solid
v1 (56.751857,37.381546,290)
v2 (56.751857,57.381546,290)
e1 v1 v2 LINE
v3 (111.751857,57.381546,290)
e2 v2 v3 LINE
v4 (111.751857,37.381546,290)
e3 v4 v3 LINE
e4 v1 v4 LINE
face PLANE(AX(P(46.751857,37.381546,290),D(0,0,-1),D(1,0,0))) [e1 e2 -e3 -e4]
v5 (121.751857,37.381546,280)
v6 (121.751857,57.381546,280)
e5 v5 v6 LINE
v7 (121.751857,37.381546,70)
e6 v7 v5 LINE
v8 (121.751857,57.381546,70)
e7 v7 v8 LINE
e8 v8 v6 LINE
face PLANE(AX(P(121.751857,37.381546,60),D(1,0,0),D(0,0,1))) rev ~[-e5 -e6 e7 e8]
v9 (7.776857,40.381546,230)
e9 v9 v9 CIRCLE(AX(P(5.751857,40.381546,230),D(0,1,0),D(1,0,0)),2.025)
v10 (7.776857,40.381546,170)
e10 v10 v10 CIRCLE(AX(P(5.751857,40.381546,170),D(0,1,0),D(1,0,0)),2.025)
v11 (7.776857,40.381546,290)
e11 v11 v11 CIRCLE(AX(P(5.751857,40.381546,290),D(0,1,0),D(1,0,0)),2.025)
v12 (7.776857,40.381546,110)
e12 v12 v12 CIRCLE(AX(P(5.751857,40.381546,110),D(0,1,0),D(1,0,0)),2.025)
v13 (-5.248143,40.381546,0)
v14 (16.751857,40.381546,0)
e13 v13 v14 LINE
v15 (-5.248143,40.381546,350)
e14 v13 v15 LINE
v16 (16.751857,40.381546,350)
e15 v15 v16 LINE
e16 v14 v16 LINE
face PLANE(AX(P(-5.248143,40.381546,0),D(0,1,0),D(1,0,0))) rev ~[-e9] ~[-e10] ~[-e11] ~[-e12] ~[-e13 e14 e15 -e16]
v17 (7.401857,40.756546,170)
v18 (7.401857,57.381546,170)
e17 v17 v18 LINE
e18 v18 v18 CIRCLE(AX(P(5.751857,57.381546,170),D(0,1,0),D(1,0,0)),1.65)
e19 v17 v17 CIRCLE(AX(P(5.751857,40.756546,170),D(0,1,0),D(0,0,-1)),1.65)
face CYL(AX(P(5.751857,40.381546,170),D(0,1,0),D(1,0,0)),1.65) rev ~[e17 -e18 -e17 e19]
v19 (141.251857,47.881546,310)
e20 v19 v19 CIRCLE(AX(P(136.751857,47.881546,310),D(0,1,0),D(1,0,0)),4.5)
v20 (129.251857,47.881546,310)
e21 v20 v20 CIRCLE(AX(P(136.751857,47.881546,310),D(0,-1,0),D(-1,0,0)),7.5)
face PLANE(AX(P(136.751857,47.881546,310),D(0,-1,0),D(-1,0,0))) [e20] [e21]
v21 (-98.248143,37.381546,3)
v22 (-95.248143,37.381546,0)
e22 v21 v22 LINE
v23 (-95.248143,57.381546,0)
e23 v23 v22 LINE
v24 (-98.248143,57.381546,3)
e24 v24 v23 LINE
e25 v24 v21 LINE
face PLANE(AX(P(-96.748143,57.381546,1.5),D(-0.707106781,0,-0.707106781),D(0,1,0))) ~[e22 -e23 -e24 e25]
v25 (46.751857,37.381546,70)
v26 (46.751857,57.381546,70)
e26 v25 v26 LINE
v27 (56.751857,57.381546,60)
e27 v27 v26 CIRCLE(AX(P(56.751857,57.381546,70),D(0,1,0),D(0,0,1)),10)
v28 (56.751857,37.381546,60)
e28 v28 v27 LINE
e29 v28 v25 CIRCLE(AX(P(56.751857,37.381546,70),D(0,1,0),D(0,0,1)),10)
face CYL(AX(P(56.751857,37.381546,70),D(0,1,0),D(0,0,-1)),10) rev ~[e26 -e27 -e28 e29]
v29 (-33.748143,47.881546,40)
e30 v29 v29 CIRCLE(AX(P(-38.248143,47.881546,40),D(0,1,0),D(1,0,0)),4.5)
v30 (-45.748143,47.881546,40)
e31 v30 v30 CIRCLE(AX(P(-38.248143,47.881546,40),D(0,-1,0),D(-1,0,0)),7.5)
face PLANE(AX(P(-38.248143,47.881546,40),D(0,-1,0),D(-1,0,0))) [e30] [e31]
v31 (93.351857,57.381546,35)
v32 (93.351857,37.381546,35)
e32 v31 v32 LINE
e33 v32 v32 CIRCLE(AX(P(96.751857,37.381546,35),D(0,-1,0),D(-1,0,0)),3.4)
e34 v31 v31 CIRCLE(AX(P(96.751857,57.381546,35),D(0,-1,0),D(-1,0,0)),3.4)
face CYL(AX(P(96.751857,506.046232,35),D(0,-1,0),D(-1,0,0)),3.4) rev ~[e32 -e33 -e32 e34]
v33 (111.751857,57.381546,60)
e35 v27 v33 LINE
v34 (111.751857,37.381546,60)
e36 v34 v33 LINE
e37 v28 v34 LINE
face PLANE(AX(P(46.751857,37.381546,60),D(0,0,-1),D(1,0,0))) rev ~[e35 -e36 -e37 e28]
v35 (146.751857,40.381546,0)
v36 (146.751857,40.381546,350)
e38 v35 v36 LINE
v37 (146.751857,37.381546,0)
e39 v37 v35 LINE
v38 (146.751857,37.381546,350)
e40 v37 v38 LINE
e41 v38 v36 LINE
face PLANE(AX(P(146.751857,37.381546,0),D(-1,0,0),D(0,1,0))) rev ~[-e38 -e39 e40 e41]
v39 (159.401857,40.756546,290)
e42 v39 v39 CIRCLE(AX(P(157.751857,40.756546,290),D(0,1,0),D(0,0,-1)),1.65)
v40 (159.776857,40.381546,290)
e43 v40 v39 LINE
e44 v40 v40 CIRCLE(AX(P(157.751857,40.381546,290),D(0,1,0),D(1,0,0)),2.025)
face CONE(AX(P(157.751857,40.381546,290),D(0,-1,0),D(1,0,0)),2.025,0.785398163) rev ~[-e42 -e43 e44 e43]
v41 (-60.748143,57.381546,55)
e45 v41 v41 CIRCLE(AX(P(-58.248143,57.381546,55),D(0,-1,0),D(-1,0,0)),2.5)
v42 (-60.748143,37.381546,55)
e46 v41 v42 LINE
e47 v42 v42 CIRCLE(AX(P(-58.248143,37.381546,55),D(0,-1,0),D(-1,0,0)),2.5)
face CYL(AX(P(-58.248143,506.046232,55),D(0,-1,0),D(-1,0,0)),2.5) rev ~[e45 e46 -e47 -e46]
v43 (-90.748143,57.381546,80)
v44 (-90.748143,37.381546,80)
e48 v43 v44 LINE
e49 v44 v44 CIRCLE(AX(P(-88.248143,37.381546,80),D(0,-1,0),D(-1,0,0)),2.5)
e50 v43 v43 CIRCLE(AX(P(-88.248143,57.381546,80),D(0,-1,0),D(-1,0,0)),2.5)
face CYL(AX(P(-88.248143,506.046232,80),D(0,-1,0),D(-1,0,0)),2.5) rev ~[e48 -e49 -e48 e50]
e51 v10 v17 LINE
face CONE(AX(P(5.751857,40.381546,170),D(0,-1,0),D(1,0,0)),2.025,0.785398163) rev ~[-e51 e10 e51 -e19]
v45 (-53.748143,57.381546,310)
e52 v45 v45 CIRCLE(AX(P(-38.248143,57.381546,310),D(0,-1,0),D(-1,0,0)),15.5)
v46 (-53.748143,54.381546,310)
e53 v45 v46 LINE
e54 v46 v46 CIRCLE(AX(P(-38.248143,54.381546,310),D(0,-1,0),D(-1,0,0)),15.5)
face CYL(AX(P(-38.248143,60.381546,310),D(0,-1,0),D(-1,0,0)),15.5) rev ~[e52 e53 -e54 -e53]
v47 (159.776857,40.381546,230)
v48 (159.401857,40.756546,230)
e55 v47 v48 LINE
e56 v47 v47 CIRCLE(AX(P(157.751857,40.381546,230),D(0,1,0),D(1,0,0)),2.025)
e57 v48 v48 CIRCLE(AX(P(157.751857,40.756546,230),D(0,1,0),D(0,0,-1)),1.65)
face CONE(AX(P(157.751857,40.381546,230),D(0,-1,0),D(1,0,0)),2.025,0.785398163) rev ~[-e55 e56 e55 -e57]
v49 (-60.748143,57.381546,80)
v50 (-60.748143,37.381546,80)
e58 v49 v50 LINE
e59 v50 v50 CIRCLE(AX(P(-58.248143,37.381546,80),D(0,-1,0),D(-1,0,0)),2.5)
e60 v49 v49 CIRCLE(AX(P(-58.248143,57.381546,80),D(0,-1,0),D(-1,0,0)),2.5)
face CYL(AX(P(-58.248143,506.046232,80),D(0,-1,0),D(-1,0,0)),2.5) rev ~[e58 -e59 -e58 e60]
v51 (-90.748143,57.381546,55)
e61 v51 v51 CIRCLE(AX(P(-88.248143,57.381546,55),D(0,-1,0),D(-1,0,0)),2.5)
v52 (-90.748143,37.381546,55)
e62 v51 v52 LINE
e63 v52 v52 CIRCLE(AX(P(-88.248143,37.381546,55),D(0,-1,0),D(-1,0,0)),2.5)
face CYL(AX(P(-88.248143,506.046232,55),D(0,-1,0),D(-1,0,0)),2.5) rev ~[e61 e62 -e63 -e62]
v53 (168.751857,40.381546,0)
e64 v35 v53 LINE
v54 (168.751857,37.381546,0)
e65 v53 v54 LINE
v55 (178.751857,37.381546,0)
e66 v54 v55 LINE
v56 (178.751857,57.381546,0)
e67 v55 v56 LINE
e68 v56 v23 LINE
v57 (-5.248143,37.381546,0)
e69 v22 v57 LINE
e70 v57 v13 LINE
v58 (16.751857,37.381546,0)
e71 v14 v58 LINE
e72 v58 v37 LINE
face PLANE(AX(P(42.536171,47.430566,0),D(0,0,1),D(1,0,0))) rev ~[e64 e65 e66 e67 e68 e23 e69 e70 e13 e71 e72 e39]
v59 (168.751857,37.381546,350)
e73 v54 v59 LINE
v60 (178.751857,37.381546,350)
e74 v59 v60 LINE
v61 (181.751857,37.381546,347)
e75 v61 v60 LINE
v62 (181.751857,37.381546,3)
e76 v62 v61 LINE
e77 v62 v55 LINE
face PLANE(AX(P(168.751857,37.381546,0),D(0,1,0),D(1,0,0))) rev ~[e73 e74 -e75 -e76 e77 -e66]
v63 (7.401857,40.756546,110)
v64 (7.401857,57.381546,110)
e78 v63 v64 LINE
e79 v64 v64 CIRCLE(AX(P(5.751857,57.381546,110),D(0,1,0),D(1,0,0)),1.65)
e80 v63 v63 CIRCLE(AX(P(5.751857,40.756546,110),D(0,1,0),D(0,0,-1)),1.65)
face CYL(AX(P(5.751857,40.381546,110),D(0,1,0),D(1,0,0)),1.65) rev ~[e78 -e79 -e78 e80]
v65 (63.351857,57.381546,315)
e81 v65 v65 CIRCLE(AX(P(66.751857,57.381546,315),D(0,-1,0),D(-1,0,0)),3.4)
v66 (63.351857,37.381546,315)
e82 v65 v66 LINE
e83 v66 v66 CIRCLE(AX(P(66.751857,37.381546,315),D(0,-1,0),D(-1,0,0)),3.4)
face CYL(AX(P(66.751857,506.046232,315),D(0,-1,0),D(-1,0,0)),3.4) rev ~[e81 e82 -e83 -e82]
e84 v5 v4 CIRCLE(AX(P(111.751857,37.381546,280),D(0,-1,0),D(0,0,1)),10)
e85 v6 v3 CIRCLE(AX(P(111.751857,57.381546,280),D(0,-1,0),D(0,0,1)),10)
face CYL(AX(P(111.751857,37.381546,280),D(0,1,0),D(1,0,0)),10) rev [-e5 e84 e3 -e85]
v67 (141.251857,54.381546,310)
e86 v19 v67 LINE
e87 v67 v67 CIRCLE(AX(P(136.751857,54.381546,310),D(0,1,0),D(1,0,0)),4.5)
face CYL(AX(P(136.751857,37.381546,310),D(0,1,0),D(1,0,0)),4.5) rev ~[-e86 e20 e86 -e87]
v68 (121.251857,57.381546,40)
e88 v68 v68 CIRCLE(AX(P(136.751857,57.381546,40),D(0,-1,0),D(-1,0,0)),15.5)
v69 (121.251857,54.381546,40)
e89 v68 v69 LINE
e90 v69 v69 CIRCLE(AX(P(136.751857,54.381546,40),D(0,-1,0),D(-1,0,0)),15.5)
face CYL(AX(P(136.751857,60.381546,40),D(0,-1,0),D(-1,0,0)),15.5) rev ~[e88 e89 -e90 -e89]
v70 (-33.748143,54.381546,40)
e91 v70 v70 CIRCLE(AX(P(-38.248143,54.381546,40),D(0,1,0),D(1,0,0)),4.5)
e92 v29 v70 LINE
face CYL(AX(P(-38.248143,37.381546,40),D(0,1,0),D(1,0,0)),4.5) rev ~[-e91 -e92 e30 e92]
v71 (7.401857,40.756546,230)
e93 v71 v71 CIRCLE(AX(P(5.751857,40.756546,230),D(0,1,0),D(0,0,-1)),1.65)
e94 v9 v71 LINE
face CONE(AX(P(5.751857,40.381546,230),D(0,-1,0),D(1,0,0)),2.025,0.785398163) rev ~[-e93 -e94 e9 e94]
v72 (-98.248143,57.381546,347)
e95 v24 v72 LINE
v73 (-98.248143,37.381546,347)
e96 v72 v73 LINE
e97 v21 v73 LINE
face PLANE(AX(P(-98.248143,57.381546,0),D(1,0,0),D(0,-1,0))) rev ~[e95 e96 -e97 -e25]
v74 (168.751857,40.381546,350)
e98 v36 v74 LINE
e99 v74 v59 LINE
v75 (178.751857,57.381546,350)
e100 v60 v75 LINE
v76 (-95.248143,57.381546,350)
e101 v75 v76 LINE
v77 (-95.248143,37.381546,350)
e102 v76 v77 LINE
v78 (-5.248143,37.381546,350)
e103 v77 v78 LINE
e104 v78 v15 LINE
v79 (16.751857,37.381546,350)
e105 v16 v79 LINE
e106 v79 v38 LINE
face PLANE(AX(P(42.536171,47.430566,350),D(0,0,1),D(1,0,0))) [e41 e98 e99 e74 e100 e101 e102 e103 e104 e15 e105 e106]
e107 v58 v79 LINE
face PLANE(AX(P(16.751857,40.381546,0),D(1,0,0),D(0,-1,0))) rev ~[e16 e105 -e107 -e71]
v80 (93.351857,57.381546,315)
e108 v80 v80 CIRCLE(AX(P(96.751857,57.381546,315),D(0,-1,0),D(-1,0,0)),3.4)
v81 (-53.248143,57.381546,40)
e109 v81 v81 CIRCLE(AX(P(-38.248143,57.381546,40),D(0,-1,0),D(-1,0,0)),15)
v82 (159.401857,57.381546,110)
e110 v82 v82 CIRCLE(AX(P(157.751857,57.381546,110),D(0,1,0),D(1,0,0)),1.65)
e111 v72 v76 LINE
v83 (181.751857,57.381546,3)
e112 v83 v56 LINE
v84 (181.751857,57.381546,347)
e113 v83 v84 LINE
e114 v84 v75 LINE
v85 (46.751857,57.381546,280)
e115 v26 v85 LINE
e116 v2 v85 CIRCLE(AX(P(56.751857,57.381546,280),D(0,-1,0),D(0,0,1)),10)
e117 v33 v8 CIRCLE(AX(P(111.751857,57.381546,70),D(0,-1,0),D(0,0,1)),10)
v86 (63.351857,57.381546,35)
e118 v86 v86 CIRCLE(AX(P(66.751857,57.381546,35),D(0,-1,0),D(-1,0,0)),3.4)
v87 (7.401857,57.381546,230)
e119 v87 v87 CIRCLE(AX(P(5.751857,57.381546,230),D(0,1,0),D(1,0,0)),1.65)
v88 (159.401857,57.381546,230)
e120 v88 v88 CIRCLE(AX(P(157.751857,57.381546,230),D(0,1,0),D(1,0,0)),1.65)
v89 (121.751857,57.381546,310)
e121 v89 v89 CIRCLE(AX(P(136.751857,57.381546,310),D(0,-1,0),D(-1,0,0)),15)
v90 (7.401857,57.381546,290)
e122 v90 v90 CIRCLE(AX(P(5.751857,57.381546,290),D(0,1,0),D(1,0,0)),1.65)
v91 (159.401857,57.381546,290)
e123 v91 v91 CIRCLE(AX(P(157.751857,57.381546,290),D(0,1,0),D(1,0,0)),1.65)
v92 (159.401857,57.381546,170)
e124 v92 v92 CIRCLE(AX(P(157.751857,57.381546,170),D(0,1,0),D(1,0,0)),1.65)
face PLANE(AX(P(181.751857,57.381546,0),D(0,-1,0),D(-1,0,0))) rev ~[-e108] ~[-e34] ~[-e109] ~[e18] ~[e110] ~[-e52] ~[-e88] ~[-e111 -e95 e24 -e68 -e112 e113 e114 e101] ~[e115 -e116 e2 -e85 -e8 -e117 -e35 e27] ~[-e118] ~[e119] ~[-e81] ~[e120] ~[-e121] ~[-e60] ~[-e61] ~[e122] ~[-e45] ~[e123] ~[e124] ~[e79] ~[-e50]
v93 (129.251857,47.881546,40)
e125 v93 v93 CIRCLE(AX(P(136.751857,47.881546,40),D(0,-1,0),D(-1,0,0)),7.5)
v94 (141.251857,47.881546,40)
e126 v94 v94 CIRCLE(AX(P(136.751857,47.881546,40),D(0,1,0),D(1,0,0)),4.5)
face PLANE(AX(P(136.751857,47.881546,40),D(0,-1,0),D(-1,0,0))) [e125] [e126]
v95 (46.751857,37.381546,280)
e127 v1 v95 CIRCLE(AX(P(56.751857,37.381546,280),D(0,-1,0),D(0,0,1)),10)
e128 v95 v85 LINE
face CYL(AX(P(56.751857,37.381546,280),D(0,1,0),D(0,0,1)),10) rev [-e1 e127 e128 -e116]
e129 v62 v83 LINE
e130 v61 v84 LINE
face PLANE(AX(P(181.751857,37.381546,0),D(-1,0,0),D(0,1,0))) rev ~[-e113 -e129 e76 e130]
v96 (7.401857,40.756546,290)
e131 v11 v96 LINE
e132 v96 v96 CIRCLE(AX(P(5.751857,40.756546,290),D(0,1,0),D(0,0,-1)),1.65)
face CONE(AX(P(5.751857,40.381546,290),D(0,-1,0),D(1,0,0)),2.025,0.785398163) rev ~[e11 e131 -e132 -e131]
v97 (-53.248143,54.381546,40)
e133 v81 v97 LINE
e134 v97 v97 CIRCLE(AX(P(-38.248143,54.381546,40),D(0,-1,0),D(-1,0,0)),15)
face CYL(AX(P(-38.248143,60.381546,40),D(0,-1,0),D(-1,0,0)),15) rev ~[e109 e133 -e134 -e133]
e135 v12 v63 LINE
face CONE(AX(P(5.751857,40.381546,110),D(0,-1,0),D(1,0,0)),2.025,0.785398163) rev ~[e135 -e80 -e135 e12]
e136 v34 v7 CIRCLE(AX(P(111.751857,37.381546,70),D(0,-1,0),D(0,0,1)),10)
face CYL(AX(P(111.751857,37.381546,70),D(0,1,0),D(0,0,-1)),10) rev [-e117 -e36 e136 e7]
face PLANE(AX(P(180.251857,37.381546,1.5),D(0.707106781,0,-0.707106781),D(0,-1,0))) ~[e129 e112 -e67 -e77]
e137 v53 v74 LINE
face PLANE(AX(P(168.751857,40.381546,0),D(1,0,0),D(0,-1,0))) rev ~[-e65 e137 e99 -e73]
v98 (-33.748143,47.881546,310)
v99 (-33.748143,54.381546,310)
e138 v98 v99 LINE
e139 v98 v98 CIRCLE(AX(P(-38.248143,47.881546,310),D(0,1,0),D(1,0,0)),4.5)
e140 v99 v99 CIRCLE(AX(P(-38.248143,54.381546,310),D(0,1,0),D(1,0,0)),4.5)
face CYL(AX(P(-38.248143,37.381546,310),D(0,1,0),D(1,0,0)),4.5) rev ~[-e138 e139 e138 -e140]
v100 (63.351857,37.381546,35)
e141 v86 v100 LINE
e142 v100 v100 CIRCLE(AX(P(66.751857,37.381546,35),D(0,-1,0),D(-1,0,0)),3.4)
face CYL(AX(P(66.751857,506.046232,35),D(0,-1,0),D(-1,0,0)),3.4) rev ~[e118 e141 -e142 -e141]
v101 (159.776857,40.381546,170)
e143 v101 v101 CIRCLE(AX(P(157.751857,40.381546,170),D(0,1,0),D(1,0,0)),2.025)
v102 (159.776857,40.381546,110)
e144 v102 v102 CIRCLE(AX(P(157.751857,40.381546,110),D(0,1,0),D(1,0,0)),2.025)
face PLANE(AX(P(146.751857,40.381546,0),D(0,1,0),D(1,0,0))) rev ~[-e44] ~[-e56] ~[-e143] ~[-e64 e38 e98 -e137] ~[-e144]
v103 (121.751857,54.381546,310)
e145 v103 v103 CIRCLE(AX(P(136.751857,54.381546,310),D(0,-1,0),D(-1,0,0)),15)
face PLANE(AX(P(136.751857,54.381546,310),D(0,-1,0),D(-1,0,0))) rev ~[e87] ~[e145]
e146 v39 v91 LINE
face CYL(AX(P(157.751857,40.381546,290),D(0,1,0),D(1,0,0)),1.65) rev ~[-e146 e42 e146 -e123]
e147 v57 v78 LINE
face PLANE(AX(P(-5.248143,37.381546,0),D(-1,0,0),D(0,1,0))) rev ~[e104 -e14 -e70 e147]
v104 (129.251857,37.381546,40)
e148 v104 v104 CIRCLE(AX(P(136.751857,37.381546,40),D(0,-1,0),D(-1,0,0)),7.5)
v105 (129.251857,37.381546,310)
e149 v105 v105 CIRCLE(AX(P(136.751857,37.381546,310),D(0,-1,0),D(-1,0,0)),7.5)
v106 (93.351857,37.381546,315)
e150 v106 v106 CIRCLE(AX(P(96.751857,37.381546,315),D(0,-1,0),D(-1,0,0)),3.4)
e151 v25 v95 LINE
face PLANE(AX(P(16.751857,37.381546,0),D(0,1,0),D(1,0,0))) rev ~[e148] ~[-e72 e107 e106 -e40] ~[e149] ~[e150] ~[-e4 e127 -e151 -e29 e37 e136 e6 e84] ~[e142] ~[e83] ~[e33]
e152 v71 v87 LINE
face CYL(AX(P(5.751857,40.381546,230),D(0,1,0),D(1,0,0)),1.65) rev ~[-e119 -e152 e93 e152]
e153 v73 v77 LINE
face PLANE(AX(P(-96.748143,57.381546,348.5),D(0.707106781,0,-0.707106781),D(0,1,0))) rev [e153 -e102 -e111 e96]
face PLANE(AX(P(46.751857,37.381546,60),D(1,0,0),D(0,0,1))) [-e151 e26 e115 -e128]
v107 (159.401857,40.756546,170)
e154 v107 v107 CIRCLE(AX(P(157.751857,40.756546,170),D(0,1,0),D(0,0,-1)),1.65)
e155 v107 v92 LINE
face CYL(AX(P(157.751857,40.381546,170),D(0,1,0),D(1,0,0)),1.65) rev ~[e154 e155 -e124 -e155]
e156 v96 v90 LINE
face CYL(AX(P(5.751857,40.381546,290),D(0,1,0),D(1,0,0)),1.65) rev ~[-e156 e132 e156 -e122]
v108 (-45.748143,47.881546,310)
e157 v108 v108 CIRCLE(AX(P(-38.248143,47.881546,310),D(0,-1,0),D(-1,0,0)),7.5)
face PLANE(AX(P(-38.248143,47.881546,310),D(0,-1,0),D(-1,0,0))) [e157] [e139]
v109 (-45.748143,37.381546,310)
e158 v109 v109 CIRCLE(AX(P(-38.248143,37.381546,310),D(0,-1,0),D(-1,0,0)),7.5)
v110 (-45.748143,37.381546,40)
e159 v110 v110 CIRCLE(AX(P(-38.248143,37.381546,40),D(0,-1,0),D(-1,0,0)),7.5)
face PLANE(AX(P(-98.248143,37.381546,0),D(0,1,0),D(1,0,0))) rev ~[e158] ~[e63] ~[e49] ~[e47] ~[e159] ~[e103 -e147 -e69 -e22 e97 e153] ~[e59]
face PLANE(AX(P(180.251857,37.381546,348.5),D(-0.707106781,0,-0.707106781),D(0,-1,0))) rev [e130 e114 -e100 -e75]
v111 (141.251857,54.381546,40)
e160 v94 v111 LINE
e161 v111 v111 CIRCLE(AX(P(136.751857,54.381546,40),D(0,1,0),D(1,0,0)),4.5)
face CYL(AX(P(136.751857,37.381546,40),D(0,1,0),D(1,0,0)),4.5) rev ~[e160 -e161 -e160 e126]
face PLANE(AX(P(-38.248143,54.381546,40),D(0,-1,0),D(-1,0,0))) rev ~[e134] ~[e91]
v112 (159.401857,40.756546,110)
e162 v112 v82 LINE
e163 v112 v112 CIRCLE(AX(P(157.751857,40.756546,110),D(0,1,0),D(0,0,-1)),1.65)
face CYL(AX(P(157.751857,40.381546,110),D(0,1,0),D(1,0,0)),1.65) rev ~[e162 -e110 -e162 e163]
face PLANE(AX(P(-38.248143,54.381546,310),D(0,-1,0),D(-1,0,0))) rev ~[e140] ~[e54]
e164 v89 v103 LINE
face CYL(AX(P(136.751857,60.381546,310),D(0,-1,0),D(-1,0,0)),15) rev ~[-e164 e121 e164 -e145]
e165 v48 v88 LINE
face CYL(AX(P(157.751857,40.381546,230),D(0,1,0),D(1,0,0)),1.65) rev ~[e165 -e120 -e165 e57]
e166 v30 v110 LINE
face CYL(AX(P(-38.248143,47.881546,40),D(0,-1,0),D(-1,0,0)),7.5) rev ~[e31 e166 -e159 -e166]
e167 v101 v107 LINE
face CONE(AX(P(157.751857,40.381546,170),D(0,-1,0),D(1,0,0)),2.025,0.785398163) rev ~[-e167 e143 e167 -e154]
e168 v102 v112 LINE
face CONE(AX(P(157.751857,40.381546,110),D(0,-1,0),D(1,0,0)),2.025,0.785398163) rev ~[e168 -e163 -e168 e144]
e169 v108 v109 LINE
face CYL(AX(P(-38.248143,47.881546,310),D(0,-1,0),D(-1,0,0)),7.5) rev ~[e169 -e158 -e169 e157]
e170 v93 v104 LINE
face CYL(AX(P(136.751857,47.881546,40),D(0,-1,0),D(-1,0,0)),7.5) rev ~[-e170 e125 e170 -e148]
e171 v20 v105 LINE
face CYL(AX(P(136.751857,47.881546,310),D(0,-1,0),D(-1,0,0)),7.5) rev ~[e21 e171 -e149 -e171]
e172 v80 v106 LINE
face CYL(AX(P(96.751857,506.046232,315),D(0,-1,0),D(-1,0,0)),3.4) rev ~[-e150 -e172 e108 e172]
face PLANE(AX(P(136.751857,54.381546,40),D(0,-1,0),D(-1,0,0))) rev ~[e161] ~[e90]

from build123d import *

# Parameters (mm, degrees)
BOSS_EXTRUDE1_DEPTH         = 350
CHAMFER1_SIZE               = 3
SKETCH2_W                   = 75
SKETCH2_H                   = 230
CUT_EXTRUDE1_DEPTH          = 395.884460879
FILLET1_R                   = 10
HOLE1_D                     = 9
HOLE1_DEPTH                 = 17
HOLE1_CBORE_D               = 15
HOLE1_CBORE_DEPTH           = 10.5
M4_TAPPED_HOLE1_D           = 3.3
M4_TAPPED_HOLE1_CSINK_D     = 4.05
M4_TAPPED_HOLE1_CSINK_ANGLE = 90
HOLE2_D                     = 31
HOLE2_DEPTH                 = 3
HOLE3_D                     = 30
HOLE3_DEPTH                 = 3
M8_TAPPED_HOLE1_D           = 6.8
M6_TAPPED_HOLE2_D           = 5


with BuildPart() as part:
    # Sketch1 → Boss-Extrude1 (new body)
    with BuildSketch(Plane.XY):
        Polygon((16.751856783, 37.381546135), (146.751856783, 37.381546135), (146.751856783, 40.381546135), (168.751856783, 40.381546135), (168.751856783, 37.381546135), (181.751856783, 37.381546135), (181.751856783, 57.381546135), (-98.248143217, 57.381546135), (-98.248143217, 37.381546135), (-5.248143217, 37.381546135), (-5.248143217, 40.381546135), (16.751856783, 40.381546135), align=None)
    extrude(amount=BOSS_EXTRUDE1_DEPTH)

    # Chamfer1
    chamfer1_edges = [part.edges().sort_by_distance(p)[0] for p in [
        (181.751856783, 47.381546135, 0),
        (-98.248143217, 47.381546135, 0),
        (181.751856783, 47.381546135, 350),
        (-98.248143217, 47.381546135, 350),
    ]]
    chamfer(chamfer1_edges, length=CHAMFER1_SIZE)

    # Sketch2 → Cut-Extrude1 (cut, through all)
    with BuildSketch(Plane.XZ.offset(-37.381546135)):
        with Locations((84.251856783, 175)):
            Rectangle(SKETCH2_W, SKETCH2_H)
    extrude(amount=-CUT_EXTRUDE1_DEPTH, mode=Mode.SUBTRACT)

    # Fillet1
    fillet1_edges = [part.edges().sort_by_distance(p)[0] for p in [
        (46.751856783, 47.381546135, 60),
        (46.751856783, 47.381546135, 290),
        (121.751856783, 47.381546135, 290),
        (121.751856783, 47.381546135, 60),
    ]]
    fillet(fillet1_edges, radius=FILLET1_R)

    # Hole1
    with Locations(Plane(origin=(0, 37.381546135, 0), x_dir=(-1, 0, 0), z_dir=(0, -1, 0))):
        with Locations((38.248143217, -310), (-136.751856783, -310), (-136.751856783, -40), (38.248143217, -40)):
            CounterBoreHole(HOLE1_D / 2, HOLE1_CBORE_D / 2, HOLE1_CBORE_DEPTH, depth=HOLE1_DEPTH)

    # M4 Tapped Hole1 (through all)
    with Locations(Plane(origin=(0, 40.381546135, 0), x_dir=(-1, 0, 0), z_dir=(0, -1, 0))):
        with Locations((-5.751856783, -290), (-5.751856783, -230), (-5.751856783, -170), (-157.751856783, -170), (-157.751856783, -230), (-157.751856783, -290), (-5.751856783, -110), (-157.751856783, -110)):
            CounterSinkHole(M4_TAPPED_HOLE1_D / 2, M4_TAPPED_HOLE1_CSINK_D / 2, counter_sink_angle=M4_TAPPED_HOLE1_CSINK_ANGLE)

    # Hole2
    with Locations(Plane(origin=(0, 57.381546135, 0), x_dir=(1, 0, 0), z_dir=(0, 1, 0))):
        with Locations((-38.248143217, -310), (136.751856783, -40)):
            Hole(HOLE2_D / 2, depth=HOLE2_DEPTH)

    # Hole3
    with Locations(Plane(origin=(0, 57.381546135, 0), x_dir=(1, 0, 0), z_dir=(0, 1, 0))):
        with Locations((-38.248143217, -40), (136.751856783, -310)):
            Hole(HOLE3_D / 2, depth=HOLE3_DEPTH)

    # M8 Tapped Hole1 (through all)
    with Locations(Plane(origin=(0, 57.381546135, 0), x_dir=(1, 0, 0), z_dir=(0, 1, 0))):
        with Locations((96.751856783, -315), (66.751856783, -315), (96.751856783, -35), (66.751856783, -35)):
            Hole(M8_TAPPED_HOLE1_D / 2)

    # M6 Tapped Hole2 (through all)
    with Locations(Plane(origin=(0, 57.381546135, 0), x_dir=(1, 0, 0), z_dir=(0, 1, 0))):
        with Locations((-58.248143217, -80), (-58.248143217, -55), (-88.248143217, -55), (-88.248143217, -80)):
            Hole(M6_TAPPED_HOLE2_D / 2)


solid = part.part
